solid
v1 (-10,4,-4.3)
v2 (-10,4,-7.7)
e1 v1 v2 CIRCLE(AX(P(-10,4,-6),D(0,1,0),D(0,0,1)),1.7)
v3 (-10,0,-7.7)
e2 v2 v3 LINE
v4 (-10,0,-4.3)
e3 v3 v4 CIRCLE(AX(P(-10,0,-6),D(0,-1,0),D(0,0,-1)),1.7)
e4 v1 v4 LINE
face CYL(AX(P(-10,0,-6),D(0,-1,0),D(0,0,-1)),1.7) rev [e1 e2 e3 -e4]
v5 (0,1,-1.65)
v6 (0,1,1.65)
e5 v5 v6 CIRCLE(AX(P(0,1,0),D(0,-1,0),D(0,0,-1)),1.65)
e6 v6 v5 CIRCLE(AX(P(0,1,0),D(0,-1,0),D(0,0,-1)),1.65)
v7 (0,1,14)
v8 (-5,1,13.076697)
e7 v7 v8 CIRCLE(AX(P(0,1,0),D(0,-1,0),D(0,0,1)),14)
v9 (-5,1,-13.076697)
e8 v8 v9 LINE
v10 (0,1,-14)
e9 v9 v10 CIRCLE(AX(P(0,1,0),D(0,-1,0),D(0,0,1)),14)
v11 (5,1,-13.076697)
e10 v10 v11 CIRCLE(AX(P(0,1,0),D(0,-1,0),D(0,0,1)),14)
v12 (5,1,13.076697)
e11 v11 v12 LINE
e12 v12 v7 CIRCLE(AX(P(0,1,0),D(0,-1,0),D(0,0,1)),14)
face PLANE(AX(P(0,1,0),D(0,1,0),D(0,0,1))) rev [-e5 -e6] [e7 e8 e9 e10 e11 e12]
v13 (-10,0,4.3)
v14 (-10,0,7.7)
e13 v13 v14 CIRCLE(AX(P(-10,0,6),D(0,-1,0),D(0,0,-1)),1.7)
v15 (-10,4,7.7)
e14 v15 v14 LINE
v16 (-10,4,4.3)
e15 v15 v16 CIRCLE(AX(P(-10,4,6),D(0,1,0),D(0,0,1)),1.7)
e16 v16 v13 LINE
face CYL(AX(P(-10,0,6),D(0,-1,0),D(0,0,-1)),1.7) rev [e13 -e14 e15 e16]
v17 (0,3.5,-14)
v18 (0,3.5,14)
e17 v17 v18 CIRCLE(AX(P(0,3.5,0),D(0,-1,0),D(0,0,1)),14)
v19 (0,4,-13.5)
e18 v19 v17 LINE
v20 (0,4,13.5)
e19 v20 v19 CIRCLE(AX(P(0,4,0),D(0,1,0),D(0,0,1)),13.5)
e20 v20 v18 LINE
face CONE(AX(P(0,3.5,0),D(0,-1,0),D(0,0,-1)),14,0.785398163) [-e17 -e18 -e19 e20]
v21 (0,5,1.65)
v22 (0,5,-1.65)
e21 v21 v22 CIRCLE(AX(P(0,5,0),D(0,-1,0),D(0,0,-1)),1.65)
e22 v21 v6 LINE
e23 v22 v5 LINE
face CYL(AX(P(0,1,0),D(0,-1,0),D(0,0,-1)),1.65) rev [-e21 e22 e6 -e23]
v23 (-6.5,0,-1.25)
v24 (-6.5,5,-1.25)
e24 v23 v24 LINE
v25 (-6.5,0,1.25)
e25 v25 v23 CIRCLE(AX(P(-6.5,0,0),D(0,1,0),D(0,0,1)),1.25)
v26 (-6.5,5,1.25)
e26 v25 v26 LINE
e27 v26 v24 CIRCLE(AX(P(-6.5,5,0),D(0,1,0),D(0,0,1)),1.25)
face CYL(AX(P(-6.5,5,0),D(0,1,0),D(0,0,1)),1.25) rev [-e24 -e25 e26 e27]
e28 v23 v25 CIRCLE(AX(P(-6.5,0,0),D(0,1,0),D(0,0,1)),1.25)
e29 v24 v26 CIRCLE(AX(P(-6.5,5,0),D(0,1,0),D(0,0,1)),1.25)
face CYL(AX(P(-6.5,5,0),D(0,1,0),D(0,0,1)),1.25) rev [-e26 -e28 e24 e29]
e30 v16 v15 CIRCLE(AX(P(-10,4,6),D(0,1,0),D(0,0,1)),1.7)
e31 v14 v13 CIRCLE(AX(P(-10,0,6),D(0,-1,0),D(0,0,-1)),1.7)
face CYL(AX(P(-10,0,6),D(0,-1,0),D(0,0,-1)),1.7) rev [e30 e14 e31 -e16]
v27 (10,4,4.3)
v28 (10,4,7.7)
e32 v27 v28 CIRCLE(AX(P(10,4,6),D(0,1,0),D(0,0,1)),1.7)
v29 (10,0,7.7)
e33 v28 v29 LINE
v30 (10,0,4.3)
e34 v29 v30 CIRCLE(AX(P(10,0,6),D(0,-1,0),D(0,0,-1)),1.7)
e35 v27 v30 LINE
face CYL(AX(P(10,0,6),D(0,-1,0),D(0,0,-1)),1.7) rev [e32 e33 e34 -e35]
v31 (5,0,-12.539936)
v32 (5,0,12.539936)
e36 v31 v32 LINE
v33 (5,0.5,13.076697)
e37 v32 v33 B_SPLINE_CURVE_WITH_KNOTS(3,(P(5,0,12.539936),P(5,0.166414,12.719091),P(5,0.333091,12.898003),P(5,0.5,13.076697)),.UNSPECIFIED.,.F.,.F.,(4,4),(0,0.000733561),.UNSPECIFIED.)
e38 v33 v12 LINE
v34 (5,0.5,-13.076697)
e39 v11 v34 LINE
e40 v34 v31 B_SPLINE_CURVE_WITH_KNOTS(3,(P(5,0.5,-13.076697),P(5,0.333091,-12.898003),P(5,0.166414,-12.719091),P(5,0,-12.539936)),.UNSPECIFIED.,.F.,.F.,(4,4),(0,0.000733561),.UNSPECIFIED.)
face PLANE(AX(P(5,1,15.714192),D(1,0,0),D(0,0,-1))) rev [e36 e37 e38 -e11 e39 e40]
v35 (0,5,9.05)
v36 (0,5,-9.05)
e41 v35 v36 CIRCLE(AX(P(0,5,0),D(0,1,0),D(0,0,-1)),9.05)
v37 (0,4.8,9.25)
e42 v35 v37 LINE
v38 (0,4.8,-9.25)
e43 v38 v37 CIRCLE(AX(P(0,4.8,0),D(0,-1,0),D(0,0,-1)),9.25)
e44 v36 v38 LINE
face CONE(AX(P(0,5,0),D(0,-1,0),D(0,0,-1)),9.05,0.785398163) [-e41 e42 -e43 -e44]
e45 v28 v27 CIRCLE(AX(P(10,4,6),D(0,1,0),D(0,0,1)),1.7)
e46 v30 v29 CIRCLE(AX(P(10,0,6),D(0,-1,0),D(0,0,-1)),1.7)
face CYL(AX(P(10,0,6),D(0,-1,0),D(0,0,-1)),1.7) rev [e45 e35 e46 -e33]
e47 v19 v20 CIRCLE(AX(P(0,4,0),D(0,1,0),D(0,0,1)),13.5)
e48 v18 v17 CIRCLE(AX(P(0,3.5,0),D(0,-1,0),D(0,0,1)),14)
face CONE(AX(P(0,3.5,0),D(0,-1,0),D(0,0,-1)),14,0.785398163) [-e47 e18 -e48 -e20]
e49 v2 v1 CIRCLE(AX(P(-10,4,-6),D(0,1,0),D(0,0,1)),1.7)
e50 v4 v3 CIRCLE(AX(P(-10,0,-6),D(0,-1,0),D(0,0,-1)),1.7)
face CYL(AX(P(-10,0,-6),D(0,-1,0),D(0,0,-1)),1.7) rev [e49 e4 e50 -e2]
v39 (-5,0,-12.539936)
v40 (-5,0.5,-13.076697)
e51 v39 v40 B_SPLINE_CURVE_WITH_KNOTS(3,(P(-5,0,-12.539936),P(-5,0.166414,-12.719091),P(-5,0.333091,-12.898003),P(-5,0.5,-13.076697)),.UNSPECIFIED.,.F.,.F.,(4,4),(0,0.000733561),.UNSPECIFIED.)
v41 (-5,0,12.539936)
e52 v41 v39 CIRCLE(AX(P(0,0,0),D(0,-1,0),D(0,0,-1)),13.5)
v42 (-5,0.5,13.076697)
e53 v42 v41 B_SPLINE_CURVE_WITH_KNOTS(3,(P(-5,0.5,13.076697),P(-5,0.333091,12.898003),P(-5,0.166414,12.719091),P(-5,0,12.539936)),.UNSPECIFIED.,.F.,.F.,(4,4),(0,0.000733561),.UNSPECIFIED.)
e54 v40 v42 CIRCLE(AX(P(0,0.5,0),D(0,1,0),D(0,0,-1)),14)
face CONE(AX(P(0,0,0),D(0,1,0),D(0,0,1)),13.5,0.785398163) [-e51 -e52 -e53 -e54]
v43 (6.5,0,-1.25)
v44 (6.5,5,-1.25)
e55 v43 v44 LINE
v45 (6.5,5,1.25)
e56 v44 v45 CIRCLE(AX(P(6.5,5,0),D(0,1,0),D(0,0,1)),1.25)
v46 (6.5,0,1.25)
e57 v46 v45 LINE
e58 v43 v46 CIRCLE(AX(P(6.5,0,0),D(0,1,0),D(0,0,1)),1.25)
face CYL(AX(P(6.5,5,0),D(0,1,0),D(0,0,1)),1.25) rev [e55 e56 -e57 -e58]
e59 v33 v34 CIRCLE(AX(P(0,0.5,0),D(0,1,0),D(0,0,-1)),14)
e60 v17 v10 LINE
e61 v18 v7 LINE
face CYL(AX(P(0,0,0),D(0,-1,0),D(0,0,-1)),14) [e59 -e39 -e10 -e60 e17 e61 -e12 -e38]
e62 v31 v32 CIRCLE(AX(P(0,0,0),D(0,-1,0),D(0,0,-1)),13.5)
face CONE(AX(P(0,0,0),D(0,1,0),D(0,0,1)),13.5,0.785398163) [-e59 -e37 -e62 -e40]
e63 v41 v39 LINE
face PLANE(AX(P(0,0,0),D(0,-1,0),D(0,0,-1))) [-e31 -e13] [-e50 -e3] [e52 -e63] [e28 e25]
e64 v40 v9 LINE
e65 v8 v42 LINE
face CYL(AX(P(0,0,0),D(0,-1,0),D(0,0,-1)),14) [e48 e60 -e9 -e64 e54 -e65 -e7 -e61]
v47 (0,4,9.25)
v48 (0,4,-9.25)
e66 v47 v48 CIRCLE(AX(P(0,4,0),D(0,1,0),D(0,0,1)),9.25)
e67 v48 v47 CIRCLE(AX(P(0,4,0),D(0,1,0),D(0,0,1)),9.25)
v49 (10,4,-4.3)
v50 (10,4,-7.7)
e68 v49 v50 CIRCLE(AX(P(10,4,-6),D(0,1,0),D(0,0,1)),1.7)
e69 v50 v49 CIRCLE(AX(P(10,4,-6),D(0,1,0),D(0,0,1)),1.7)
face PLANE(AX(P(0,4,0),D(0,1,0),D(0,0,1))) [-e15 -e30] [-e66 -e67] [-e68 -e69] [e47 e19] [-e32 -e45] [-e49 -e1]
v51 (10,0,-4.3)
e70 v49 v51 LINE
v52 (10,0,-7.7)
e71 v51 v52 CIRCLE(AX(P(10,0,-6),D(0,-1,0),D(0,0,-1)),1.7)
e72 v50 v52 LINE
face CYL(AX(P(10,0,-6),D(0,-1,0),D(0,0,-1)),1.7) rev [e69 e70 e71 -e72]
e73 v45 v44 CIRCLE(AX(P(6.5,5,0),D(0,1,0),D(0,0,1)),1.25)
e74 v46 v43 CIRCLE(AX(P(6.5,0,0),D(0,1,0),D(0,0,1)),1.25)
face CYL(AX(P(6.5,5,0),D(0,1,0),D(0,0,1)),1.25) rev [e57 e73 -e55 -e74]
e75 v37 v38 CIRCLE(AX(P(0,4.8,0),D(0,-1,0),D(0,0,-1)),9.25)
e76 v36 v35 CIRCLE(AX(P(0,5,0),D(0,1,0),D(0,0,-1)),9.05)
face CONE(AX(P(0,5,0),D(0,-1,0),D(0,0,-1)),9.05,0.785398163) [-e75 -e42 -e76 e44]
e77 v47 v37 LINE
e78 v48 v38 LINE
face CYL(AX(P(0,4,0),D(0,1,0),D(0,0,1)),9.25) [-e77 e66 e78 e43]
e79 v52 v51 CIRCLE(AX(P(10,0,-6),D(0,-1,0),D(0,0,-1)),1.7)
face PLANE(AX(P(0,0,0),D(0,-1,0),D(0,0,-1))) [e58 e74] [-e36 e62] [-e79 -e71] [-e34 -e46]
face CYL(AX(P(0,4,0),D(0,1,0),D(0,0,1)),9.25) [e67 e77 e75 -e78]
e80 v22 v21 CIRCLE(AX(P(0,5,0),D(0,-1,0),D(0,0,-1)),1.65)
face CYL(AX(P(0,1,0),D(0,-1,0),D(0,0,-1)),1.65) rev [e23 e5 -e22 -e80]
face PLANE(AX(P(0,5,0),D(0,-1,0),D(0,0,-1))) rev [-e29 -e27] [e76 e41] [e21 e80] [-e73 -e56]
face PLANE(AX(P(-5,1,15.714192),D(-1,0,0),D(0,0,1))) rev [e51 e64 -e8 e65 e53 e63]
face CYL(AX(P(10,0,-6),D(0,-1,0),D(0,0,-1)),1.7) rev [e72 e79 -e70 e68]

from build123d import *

# Parameters (mm, degrees)
M3_TAPPED_HOLE1_D    = 2.5
SKETCH3_OUTSIDE_W    = 37.982
SKETCH3_OUTSIDE_H    = 37.982
SKETCH3_OUTSIDE_R    = 9.25
CUT_EXTRUDE2_DEPTH   = 1
M3_CLEARANCE_HOLE1_D = 3.4
SKETCH6_W            = 10
SKETCH6_H            = 31.428384658
CUT_EXTRUDE3_DEPTH   = 1
M4_TAPPED_HOLE1_D    = 3.3
CHAMFER1_SIZE        = 0.5
CHAMFER2_SIZE        = 0.2


with BuildPart() as part:
    # Sketch1 → Revolve1 (revolve)
    with BuildSketch(Plane.XY, mode=Mode.PRIVATE) as revolve1_sk:
        Polygon((4.5, 5), (6, 5), (14, 5), (14, 0), (0, 0), (0, 5), align=None)
    revolve(revolve1_sk.sketch.rotate(Axis((0, 0, 0), (0, 1, 0)), 90), axis=Axis((0, 0, 0), (0, 1, 0)))

    # M3 Tapped Hole1 (through all)
    with Locations(Plane(origin=(0, 5, 0), x_dir=(1, 0, 0), z_dir=(0, 1, 0))):
        with Locations((-6.5, 0), (6.5, 0)):
            Hole(M3_TAPPED_HOLE1_D / 2)

    # Sketch3 outside → Cut-Extrude2 (cut)
    with BuildSketch(Plane(origin=(0, 5, 0), x_dir=(1, 0, 0), z_dir=(0, 1, 0))):
        Rectangle(SKETCH3_OUTSIDE_W, SKETCH3_OUTSIDE_H)
        with Locations(Location((0, 0, 0), (0, 0, 270))):
            Circle(SKETCH3_OUTSIDE_R, mode=Mode.SUBTRACT)
    extrude(amount=-CUT_EXTRUDE2_DEPTH, mode=Mode.SUBTRACT)

    # M3 Clearance Hole1 (through all)
    with Locations(Plane(origin=(0, 0, 0), x_dir=(-1, 0, 0), z_dir=(0, -1, 0))):
        with Locations((10, -6), (10, 6), (-10, -6), (-10, 6)):
            Hole(M3_CLEARANCE_HOLE1_D / 2)

    # Sketch6 → Cut-Extrude3 (cut)
    with BuildSketch(Plane.XZ):
        Rectangle(SKETCH6_W, SKETCH6_H)
    extrude(amount=-CUT_EXTRUDE3_DEPTH, mode=Mode.SUBTRACT)

    # M4 Tapped Hole1 (through all)
    with Locations(Plane(origin=(0, 1, 0), x_dir=(-1, 0, 0), z_dir=(0, -1, 0))):
        with Locations((0, 0)):
            Hole(M4_TAPPED_HOLE1_D / 2)

    # Chamfer1
    chamfer1_edges = [part.edges().sort_by_distance(p)[0] for p in [
        (0, 4, 14),
        (14, 0, 0),
        (-14, 0, 0),
    ]]
    chamfer(chamfer1_edges, length=CHAMFER1_SIZE)

    # Chamfer2
    chamfer2_edges = [part.edges().sort_by_distance(p)[0] for p in [
        (0, 5, -9.25),
    ]]
    chamfer(chamfer2_edges, length=CHAMFER2_SIZE)


solid = part.part
